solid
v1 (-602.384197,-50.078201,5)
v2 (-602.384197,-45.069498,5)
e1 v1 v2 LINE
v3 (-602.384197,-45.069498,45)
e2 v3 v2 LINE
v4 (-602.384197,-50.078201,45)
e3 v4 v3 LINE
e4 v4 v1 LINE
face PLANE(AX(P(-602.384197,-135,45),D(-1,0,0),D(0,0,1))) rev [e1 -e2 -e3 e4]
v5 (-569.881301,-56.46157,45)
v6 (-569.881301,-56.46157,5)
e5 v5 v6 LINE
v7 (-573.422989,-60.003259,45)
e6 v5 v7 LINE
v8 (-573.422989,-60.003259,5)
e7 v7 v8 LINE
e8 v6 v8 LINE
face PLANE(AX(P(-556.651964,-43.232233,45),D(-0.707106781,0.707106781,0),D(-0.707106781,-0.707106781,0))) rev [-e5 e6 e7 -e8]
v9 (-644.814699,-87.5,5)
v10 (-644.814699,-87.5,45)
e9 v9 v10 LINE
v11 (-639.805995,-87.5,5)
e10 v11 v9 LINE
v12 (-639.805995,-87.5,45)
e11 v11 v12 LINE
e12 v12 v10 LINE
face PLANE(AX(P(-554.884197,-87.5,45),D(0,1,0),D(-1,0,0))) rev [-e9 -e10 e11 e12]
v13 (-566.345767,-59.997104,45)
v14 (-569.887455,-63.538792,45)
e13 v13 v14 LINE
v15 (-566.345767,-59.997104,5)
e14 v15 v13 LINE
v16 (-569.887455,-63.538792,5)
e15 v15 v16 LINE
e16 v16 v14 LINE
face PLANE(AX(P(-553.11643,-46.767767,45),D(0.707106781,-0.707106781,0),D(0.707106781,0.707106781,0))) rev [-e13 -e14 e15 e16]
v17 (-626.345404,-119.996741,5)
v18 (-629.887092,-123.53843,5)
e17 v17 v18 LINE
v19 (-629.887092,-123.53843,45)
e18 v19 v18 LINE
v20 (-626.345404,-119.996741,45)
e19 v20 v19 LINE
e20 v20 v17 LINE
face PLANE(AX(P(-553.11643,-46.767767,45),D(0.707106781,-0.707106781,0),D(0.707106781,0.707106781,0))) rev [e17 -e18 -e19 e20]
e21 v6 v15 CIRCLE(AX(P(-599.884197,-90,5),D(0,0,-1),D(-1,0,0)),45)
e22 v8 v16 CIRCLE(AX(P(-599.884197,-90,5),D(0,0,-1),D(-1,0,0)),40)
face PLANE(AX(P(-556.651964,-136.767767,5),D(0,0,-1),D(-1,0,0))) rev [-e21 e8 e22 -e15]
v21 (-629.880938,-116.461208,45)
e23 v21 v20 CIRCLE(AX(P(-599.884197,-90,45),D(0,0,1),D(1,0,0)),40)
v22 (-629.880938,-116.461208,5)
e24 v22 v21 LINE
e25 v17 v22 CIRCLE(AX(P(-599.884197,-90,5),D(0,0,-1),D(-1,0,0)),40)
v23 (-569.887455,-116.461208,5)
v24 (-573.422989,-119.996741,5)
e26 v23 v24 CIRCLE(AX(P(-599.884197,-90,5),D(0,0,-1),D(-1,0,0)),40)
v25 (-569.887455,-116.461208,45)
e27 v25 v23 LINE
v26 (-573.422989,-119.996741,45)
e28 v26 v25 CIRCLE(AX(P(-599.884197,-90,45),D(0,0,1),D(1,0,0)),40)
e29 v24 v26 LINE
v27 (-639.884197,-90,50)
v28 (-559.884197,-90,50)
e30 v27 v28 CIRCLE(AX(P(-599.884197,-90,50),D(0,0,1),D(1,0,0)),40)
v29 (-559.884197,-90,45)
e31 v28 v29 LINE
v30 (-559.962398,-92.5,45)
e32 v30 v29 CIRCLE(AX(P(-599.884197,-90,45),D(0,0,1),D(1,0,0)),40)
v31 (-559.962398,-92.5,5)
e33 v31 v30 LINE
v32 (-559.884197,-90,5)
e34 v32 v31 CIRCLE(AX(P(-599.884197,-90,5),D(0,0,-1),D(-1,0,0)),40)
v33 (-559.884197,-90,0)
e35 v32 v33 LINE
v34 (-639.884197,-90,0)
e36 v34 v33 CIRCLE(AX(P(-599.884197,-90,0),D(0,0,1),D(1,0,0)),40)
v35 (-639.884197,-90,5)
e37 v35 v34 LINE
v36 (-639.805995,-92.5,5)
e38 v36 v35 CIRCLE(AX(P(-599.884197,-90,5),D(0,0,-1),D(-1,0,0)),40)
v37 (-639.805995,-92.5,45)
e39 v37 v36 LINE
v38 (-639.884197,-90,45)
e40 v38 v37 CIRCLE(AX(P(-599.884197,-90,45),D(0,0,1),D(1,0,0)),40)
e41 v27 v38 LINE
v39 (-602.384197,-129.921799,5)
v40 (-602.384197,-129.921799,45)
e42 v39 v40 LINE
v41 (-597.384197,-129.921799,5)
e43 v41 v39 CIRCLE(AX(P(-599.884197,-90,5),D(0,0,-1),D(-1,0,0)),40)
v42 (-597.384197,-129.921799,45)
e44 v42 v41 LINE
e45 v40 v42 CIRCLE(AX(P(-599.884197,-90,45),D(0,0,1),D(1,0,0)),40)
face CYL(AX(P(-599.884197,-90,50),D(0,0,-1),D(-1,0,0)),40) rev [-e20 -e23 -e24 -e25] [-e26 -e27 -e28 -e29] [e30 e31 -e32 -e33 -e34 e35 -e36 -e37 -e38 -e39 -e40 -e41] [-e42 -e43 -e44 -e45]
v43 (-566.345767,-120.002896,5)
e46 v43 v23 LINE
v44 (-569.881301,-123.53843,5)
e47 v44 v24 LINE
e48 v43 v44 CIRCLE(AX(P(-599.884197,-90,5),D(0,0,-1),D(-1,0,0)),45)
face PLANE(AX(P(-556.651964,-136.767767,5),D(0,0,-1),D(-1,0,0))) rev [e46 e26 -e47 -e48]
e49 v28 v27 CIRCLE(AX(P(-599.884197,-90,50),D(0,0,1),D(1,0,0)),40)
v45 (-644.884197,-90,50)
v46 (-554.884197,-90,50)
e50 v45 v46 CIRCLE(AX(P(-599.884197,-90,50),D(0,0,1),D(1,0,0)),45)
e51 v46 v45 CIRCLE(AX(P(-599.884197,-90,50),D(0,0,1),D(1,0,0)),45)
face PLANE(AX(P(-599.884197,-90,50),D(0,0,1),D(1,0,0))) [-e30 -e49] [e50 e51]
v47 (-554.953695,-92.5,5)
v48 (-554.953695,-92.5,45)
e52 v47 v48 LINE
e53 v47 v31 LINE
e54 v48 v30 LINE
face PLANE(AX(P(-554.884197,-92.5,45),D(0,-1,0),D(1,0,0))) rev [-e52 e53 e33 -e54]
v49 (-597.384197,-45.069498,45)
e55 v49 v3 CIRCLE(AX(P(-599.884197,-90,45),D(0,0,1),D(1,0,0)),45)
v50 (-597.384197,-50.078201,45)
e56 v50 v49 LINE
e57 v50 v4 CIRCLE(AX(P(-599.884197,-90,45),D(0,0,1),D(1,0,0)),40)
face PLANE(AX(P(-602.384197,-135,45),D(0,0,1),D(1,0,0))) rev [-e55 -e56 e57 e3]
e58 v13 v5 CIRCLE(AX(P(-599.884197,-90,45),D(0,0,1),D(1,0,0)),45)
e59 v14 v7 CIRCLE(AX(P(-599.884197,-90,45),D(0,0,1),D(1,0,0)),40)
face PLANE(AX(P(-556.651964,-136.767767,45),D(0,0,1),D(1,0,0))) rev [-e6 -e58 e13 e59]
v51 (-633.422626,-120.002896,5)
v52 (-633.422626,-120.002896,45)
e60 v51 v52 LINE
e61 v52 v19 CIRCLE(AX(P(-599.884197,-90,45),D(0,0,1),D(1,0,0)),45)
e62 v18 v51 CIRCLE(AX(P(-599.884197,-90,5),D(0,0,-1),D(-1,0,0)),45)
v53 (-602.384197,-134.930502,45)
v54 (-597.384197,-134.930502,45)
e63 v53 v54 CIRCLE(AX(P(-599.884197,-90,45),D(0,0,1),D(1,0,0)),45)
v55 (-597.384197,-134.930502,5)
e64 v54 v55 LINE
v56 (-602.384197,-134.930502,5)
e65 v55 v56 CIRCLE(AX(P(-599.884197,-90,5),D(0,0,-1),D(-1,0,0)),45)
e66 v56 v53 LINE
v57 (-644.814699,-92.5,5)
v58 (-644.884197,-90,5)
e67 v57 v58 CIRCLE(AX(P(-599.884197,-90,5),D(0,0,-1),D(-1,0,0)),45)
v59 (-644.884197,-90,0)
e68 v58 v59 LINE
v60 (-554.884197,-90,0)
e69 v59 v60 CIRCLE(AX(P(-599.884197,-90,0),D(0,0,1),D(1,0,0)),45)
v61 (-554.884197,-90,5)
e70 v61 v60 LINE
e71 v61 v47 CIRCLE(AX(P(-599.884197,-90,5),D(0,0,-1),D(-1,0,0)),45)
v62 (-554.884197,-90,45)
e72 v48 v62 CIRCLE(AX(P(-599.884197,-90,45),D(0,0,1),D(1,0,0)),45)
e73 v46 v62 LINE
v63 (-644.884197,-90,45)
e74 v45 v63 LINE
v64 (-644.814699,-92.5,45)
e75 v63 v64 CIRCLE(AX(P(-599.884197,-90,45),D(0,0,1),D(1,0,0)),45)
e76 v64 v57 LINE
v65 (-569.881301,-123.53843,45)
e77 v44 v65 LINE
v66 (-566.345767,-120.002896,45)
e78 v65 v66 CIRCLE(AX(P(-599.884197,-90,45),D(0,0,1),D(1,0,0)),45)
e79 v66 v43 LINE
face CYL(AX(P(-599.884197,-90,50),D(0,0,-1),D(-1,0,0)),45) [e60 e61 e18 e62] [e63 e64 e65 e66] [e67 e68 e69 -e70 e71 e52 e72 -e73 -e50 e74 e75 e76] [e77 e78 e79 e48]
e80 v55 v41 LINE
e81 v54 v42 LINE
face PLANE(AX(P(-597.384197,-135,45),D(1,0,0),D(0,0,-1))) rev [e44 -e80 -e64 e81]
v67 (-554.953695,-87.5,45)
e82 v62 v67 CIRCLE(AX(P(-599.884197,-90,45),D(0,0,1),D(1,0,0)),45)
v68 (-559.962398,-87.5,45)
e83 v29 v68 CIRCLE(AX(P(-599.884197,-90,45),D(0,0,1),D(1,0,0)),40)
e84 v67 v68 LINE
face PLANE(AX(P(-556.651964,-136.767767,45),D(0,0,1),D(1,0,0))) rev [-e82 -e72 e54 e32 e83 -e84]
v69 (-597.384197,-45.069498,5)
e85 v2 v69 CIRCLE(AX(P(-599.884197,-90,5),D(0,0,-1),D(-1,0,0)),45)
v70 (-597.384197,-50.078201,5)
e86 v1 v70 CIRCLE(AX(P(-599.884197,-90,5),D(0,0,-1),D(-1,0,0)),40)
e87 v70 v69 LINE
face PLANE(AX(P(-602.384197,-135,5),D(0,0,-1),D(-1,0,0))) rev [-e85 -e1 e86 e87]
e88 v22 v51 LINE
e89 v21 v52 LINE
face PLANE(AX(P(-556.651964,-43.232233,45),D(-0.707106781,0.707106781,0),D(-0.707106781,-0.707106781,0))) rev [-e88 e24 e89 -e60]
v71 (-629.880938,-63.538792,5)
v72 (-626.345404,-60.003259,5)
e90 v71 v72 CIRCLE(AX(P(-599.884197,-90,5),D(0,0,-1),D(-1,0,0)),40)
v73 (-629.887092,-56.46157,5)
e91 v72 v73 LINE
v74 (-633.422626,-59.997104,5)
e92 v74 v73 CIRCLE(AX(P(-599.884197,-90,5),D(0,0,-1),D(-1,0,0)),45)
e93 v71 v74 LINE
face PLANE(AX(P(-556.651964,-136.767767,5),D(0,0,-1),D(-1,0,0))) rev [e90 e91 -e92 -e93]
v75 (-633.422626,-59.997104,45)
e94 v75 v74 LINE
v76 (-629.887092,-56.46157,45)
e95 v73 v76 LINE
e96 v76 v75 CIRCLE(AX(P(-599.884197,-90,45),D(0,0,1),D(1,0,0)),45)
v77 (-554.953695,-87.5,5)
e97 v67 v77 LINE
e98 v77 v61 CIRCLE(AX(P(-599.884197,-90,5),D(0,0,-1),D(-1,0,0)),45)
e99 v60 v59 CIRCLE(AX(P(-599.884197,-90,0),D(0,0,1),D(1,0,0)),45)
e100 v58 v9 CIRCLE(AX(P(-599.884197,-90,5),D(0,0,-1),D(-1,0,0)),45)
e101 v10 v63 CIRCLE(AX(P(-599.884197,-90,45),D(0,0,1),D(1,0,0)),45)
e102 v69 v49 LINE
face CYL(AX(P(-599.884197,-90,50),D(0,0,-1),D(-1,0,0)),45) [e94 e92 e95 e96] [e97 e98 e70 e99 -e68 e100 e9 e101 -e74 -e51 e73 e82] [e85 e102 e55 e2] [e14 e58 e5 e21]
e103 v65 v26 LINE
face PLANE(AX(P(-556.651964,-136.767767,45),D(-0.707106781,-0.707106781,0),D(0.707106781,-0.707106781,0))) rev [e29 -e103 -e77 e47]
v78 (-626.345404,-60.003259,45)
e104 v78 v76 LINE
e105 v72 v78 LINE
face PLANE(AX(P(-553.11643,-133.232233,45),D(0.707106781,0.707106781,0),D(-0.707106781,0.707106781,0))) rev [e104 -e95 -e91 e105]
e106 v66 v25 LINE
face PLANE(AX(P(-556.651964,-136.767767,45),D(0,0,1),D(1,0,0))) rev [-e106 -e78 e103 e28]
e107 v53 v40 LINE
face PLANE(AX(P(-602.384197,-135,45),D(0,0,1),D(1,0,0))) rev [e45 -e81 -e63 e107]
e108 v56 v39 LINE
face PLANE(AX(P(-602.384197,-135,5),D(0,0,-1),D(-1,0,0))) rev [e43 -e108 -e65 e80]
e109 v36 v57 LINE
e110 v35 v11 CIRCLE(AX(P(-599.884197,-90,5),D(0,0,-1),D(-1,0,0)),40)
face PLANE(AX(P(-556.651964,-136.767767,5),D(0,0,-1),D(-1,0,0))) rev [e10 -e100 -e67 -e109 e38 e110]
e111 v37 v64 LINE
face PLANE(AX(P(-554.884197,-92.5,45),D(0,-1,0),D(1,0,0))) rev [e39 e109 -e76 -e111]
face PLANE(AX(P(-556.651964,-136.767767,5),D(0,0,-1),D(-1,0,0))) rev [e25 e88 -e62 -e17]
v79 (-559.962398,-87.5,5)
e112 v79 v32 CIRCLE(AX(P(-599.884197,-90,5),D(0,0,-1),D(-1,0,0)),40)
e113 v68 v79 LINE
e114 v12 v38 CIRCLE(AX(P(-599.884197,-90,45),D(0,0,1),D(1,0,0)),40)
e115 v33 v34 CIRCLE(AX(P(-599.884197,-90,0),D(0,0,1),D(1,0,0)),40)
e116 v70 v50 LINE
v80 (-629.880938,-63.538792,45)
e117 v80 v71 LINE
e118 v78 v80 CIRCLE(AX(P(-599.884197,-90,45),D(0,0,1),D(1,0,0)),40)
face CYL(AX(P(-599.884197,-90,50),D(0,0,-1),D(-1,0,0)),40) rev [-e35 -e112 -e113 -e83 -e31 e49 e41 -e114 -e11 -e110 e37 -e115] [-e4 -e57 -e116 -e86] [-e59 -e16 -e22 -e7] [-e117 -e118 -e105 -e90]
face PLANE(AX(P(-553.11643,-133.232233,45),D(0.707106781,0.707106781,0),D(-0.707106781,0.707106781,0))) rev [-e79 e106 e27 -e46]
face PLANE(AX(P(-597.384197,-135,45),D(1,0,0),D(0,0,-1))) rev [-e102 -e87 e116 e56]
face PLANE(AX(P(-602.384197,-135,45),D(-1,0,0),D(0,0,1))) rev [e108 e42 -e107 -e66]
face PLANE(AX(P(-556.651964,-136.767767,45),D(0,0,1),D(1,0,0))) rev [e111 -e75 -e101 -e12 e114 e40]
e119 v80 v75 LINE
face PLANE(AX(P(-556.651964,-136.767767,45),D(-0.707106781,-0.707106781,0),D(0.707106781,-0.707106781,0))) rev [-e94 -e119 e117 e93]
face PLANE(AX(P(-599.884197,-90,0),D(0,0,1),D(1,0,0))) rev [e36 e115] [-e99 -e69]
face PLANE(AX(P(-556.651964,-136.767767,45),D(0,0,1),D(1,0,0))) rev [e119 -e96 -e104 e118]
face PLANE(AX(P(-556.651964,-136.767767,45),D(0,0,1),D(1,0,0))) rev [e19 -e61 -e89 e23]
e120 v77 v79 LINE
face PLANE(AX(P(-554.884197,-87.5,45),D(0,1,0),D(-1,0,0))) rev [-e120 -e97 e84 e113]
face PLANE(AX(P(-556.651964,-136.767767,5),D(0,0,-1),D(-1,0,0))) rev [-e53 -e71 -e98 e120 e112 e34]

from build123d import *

# Parameters (mm, degrees)
SKETCH1_R           = 45
SKETCH1_R_2         = 40
BOSS_EXTRUDE1_DEPTH = 50
SKETCH2_W           = 5
SKETCH2_H           = 40
CUT_EXTRUDE1_DEPTH  = 661.757616096
CIRPATTERN1_COUNT   = 8


with BuildPart() as part:
    # Sketch1 → Boss-Extrude1 (new body)
    with BuildSketch(Plane.XY):
        with Locations((-599.884196758, -90)):
            Circle(SKETCH1_R)
        with Locations((-599.884196758, -90)):
            Circle(SKETCH1_R_2, mode=Mode.SUBTRACT)
    extrude(amount=BOSS_EXTRUDE1_DEPTH)

    # Sketch2 → Cut-Extrude1 (cut, symmetric)
    with BuildSketch(Plane(origin=(0, 0, 0), x_dir=(1, 0, 0), z_dir=(0, 1, 0))):
        with Locations((-599.884196758, -25)):
            Rectangle(SKETCH2_W, SKETCH2_H)
    cut_extrude1 = extrude(amount=CUT_EXTRUDE1_DEPTH, both=True, mode=Mode.SUBTRACT)

    # CirPattern1: Cut-Extrude1 ×8 about axis
    cirpattern1_axis = Axis((-599.884196758, -90, 0), (0, 0, 1))
    for i in range(1, CIRPATTERN1_COUNT):
        add(cut_extrude1.rotate(cirpattern1_axis, i * 360 / CIRPATTERN1_COUNT), mode=Mode.SUBTRACT)


solid = part.part
